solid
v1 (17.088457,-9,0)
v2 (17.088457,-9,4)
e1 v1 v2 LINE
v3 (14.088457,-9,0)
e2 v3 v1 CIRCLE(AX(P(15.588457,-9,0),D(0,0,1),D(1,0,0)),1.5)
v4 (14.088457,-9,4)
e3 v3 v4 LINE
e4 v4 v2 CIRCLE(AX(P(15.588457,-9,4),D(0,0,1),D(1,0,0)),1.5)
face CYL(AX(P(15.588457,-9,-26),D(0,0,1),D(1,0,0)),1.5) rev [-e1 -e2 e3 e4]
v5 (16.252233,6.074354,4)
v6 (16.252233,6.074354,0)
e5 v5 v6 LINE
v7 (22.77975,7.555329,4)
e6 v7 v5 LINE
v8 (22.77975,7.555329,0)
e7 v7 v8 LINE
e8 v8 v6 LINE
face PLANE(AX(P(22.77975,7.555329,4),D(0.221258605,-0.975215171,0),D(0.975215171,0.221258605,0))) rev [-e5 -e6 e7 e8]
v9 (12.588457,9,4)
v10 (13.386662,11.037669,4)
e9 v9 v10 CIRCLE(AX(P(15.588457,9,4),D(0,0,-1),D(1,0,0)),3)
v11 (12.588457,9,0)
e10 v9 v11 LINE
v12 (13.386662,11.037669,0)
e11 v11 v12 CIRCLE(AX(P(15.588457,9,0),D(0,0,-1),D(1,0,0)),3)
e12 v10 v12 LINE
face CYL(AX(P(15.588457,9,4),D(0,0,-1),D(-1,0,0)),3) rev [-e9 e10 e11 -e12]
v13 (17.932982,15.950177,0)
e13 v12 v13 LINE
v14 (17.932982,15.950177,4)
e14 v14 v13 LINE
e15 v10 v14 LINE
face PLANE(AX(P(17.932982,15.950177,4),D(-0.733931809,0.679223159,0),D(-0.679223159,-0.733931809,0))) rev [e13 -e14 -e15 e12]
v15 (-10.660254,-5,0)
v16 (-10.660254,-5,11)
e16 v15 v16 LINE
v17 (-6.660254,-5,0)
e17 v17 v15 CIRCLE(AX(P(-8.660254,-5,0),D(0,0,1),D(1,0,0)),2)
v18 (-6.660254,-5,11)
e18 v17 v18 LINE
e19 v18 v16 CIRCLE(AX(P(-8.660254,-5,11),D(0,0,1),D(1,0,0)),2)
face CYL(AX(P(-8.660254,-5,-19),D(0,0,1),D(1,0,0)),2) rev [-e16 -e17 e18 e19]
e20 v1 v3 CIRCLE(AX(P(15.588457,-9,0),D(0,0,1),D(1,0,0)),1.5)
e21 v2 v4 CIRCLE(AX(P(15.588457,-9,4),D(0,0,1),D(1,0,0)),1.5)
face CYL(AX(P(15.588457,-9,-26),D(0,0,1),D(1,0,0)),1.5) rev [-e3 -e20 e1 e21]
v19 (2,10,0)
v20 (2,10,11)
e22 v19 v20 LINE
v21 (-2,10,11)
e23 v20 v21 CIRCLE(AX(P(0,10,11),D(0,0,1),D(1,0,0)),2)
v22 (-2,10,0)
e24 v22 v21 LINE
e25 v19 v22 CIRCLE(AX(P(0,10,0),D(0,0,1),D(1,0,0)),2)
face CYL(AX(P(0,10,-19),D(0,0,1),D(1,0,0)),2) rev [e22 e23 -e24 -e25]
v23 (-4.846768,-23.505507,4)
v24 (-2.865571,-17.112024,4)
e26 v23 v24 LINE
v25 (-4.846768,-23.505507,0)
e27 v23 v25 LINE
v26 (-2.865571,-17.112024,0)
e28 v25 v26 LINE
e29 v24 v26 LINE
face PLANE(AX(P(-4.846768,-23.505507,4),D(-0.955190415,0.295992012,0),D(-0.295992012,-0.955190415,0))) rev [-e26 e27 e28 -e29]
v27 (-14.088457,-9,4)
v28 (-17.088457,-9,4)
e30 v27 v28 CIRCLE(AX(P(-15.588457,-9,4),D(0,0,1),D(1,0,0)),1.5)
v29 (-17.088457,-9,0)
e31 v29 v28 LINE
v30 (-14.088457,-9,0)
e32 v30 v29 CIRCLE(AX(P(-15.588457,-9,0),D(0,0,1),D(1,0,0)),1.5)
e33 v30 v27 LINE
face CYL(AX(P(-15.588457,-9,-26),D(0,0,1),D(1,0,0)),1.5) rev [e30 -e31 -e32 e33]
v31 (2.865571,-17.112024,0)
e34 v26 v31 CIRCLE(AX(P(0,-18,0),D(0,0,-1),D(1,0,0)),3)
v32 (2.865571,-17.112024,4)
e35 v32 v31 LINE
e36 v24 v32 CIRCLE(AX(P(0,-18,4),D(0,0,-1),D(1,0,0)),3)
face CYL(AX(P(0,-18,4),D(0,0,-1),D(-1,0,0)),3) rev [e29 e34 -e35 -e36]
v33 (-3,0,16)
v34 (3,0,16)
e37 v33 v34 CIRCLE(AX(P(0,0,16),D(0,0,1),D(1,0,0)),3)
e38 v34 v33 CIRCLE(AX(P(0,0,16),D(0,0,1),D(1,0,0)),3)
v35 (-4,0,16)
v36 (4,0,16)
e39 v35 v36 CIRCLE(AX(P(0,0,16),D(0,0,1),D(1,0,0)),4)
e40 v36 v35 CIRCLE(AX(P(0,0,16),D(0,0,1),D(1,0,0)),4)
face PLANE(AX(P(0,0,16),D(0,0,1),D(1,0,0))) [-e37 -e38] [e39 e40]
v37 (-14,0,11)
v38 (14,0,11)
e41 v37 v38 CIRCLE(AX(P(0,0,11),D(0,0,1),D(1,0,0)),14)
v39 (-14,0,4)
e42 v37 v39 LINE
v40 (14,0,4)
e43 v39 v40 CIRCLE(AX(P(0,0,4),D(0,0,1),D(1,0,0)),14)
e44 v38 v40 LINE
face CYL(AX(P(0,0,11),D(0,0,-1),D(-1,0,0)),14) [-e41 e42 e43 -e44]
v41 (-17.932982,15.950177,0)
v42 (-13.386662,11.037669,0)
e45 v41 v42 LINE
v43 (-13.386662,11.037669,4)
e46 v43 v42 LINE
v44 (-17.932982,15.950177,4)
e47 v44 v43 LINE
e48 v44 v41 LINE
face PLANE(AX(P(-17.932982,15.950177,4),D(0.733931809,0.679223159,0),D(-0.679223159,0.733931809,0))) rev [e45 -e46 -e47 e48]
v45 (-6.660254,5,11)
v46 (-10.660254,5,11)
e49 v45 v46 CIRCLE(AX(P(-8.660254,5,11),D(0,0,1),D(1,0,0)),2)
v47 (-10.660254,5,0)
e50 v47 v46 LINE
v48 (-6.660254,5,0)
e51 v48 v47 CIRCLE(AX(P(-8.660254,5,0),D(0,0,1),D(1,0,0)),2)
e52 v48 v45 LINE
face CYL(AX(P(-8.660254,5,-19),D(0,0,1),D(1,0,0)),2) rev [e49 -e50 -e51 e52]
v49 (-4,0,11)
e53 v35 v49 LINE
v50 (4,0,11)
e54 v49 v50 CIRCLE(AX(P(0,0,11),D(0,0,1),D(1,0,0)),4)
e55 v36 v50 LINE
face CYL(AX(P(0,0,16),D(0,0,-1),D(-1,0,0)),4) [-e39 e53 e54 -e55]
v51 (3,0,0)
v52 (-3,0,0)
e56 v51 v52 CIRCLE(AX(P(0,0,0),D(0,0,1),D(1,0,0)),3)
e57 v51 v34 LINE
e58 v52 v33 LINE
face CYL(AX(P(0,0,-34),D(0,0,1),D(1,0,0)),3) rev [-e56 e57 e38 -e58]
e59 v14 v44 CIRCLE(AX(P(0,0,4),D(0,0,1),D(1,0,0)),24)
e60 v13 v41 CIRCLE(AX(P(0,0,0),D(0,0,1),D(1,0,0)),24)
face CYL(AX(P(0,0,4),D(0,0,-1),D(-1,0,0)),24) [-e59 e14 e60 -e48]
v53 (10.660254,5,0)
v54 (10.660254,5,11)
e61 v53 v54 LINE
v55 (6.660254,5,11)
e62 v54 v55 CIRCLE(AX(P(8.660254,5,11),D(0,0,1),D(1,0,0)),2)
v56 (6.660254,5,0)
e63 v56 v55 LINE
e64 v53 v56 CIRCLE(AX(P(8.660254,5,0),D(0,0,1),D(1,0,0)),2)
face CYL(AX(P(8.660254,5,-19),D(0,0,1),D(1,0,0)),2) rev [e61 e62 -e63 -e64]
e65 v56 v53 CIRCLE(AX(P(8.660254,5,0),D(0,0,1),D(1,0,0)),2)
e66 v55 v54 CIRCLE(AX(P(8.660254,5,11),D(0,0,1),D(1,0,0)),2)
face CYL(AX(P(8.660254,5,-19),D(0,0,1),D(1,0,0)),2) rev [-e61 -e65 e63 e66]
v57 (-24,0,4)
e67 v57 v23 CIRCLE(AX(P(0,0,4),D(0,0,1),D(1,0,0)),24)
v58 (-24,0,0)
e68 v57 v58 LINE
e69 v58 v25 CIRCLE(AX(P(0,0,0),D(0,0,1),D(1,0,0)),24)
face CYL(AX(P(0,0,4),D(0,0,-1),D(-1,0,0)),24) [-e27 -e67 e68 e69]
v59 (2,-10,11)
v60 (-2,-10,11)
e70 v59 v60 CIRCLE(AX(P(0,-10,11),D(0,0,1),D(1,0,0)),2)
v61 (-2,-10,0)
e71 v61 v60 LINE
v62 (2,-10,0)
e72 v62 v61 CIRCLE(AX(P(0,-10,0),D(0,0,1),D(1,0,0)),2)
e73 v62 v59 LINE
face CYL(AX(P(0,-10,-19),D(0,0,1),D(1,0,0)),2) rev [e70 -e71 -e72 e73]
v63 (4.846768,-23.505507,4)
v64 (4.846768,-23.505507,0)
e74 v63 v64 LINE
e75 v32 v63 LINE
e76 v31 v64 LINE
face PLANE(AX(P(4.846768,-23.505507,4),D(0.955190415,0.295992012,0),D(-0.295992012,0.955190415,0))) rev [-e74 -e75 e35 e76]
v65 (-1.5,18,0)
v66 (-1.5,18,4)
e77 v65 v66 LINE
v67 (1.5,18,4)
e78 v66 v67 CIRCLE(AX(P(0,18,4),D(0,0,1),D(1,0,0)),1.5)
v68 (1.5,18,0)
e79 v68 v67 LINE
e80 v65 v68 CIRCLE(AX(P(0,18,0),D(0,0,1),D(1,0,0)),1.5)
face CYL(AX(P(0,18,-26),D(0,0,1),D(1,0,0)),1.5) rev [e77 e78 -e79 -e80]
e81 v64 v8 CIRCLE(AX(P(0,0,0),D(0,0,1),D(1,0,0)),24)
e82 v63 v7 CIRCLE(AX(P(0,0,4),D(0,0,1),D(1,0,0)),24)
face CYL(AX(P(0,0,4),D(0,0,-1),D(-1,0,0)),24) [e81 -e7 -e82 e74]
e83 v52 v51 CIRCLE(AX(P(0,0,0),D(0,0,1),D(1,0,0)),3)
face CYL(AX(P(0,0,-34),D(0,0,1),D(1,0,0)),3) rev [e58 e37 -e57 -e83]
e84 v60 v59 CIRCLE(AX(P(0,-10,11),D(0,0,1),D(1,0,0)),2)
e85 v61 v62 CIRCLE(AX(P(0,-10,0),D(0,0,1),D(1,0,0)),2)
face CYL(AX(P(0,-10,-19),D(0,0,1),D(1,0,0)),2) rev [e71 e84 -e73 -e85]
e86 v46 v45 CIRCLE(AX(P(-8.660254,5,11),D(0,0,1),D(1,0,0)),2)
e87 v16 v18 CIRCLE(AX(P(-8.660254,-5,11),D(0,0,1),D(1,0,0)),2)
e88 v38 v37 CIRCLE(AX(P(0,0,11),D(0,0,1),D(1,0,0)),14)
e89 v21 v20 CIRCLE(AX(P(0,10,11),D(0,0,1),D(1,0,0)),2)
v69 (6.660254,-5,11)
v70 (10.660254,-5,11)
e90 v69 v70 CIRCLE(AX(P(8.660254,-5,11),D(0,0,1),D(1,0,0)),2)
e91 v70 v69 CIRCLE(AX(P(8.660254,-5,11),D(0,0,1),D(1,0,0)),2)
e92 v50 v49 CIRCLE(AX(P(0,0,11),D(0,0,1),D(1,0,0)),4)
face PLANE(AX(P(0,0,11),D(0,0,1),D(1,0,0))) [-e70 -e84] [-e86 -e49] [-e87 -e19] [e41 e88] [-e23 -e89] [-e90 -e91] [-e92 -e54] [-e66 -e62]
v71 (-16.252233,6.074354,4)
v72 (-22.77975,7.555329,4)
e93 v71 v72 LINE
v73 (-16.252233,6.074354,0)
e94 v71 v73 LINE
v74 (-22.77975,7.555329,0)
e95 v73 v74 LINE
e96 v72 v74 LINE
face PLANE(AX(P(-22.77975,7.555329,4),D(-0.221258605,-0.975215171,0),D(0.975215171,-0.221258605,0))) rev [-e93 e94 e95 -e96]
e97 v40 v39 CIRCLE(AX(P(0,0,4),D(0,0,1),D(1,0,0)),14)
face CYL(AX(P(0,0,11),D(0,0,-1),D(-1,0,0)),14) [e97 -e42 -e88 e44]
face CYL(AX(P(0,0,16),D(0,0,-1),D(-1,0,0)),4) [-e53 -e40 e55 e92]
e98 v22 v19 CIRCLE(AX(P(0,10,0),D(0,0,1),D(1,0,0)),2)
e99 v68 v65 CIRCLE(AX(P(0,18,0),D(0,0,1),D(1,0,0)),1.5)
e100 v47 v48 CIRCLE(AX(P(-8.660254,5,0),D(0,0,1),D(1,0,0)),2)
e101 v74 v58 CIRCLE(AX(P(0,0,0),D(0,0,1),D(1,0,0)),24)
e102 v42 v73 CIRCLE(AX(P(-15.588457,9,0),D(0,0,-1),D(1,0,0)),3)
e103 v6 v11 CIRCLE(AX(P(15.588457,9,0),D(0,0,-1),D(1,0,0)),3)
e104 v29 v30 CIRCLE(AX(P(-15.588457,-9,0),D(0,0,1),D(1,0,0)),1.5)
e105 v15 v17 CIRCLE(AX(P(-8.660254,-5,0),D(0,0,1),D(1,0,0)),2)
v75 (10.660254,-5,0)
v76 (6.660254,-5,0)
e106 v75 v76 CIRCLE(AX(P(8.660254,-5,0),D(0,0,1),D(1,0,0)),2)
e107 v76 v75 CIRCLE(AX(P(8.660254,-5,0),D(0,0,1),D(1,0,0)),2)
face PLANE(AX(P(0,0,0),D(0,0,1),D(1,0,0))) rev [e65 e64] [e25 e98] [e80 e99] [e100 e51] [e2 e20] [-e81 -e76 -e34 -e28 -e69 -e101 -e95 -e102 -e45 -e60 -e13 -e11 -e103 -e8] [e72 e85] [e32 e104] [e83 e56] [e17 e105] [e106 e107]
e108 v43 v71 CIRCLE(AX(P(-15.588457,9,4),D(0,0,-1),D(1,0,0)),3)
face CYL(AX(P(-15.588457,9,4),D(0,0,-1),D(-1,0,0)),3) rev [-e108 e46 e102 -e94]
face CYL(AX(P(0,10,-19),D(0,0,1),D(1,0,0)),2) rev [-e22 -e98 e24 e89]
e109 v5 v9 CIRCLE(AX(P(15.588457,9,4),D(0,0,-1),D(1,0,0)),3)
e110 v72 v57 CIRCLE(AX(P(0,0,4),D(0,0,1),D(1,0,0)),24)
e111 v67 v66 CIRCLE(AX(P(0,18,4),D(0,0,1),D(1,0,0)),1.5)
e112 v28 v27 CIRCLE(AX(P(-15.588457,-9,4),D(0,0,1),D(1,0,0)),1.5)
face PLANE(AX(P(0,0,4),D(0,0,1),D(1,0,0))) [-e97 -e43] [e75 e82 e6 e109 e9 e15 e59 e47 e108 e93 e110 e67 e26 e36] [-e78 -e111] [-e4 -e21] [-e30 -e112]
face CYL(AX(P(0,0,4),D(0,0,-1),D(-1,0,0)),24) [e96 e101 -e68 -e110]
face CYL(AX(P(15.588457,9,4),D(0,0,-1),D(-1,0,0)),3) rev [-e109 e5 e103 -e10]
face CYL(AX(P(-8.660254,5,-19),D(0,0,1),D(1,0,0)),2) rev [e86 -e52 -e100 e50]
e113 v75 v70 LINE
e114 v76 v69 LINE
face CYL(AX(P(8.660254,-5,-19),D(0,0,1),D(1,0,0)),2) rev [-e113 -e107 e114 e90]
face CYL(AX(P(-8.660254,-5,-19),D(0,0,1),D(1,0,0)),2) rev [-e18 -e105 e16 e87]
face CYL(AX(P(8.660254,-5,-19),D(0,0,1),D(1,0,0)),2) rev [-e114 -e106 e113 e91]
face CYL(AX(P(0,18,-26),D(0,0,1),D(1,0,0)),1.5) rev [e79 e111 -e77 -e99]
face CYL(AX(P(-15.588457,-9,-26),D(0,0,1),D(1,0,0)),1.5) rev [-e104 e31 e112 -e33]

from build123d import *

# Parameters (mm, degrees)
SLOTTED_FLANGE_48_DEPTH = 4
HUB_SKETCH_R            = 14
HUB_28_DEPTH            = 7
HUB_HOLES_SKETCH_R      = 2
HUB_HOLES_6X_4_DEPTH    = 30
SPIGOT_SKETCH_R         = 4
SPIGOT_8_DEPTH          = 5
BORE_SKETCH_R           = 3
BORE_6_DEPTH            = 50
FLANGE_HOLES_SKETCH_R   = 1.5
FLANGE_HOLES_3X_3_DEPTH = 30


with BuildPart() as part:
    # Flange Profile Sketch → Slotted Flange Ø48 (new body)
    with BuildSketch(Plane.XY):
        with BuildLine():
            Line((4.846767643, -23.505506661), (2.865571245, -17.112023963))
            ThreePointArc((2.865571245, -17.112023963), (0, -15), (-2.865571245, -17.112023963))
            Line((-2.865571245, -17.112023963), (-4.846767643, -23.505506661))
            ThreePointArc((-4.846767643, -23.505506661), (-20.784609691, -12), (-22.779749719, 7.555329425))
            Line((-22.779749719, 7.555329425), (-16.252233084, 6.074354487))
            ThreePointArc((-16.252233084, 6.074354487), (-12.990381057, 7.5), (-13.38666184, 11.037669476))
            Line((-13.38666184, 11.037669476), (-17.932982076, 15.950177236))
            ThreePointArc((-17.932982076, 15.950177236), (0, 24), (17.932982076, 15.950177236))
            Line((17.932982076, 15.950177236), (13.38666184, 11.037669476))
            ThreePointArc((13.38666184, 11.037669476), (12.990381057, 7.5), (16.252233084, 6.074354487))
            Line((16.252233084, 6.074354487), (22.779749719, 7.555329425))
            ThreePointArc((22.779749719, 7.555329425), (20.784609691, -12), (4.846767643, -23.505506661))
        make_face()
    extrude(amount=SLOTTED_FLANGE_48_DEPTH)

    # Hub Sketch → Hub Ø28 (add)
    with BuildSketch(Plane.XY.offset(4)):
        Circle(HUB_SKETCH_R)
    extrude(amount=HUB_28_DEPTH)

    # Hub Holes Sketch → Hub Holes 6xØ4 (cut)
    with BuildSketch(Plane.XY.offset(11)):
        with Locations((0, 10)):
            Circle(HUB_HOLES_SKETCH_R)
        with Locations((8.660254038, 5)):
            Circle(HUB_HOLES_SKETCH_R)
        with Locations((8.660254038, -5)):
            Circle(HUB_HOLES_SKETCH_R)
        with Locations((0, -10)):
            Circle(HUB_HOLES_SKETCH_R)
        with Locations((-8.660254038, -5)):
            Circle(HUB_HOLES_SKETCH_R)
        with Locations((-8.660254038, 5)):
            Circle(HUB_HOLES_SKETCH_R)
    extrude(amount=-HUB_HOLES_6X_4_DEPTH, mode=Mode.SUBTRACT)

    # Spigot Sketch → Spigot Ø8 (add)
    with BuildSketch(Plane.XY.offset(11)):
        Circle(SPIGOT_SKETCH_R)
    extrude(amount=SPIGOT_8_DEPTH)

    # Bore Sketch → Bore Ø6 (cut)
    with BuildSketch(Plane.XY.offset(16)):
        Circle(BORE_SKETCH_R)
    extrude(amount=-BORE_6_DEPTH, mode=Mode.SUBTRACT)

    # Flange Holes Sketch → Flange Holes 3xØ3 (cut)
    with BuildSketch(Plane.XY.offset(4)):
        with Locations((15.588457268, -9)):
            Circle(FLANGE_HOLES_SKETCH_R)
        with Locations((0, 18)):
            Circle(FLANGE_HOLES_SKETCH_R)
        with Locations((-15.588457268, -9)):
            Circle(FLANGE_HOLES_SKETCH_R)
    extrude(amount=-FLANGE_HOLES_3X_3_DEPTH, mode=Mode.SUBTRACT)


solid = part.part
